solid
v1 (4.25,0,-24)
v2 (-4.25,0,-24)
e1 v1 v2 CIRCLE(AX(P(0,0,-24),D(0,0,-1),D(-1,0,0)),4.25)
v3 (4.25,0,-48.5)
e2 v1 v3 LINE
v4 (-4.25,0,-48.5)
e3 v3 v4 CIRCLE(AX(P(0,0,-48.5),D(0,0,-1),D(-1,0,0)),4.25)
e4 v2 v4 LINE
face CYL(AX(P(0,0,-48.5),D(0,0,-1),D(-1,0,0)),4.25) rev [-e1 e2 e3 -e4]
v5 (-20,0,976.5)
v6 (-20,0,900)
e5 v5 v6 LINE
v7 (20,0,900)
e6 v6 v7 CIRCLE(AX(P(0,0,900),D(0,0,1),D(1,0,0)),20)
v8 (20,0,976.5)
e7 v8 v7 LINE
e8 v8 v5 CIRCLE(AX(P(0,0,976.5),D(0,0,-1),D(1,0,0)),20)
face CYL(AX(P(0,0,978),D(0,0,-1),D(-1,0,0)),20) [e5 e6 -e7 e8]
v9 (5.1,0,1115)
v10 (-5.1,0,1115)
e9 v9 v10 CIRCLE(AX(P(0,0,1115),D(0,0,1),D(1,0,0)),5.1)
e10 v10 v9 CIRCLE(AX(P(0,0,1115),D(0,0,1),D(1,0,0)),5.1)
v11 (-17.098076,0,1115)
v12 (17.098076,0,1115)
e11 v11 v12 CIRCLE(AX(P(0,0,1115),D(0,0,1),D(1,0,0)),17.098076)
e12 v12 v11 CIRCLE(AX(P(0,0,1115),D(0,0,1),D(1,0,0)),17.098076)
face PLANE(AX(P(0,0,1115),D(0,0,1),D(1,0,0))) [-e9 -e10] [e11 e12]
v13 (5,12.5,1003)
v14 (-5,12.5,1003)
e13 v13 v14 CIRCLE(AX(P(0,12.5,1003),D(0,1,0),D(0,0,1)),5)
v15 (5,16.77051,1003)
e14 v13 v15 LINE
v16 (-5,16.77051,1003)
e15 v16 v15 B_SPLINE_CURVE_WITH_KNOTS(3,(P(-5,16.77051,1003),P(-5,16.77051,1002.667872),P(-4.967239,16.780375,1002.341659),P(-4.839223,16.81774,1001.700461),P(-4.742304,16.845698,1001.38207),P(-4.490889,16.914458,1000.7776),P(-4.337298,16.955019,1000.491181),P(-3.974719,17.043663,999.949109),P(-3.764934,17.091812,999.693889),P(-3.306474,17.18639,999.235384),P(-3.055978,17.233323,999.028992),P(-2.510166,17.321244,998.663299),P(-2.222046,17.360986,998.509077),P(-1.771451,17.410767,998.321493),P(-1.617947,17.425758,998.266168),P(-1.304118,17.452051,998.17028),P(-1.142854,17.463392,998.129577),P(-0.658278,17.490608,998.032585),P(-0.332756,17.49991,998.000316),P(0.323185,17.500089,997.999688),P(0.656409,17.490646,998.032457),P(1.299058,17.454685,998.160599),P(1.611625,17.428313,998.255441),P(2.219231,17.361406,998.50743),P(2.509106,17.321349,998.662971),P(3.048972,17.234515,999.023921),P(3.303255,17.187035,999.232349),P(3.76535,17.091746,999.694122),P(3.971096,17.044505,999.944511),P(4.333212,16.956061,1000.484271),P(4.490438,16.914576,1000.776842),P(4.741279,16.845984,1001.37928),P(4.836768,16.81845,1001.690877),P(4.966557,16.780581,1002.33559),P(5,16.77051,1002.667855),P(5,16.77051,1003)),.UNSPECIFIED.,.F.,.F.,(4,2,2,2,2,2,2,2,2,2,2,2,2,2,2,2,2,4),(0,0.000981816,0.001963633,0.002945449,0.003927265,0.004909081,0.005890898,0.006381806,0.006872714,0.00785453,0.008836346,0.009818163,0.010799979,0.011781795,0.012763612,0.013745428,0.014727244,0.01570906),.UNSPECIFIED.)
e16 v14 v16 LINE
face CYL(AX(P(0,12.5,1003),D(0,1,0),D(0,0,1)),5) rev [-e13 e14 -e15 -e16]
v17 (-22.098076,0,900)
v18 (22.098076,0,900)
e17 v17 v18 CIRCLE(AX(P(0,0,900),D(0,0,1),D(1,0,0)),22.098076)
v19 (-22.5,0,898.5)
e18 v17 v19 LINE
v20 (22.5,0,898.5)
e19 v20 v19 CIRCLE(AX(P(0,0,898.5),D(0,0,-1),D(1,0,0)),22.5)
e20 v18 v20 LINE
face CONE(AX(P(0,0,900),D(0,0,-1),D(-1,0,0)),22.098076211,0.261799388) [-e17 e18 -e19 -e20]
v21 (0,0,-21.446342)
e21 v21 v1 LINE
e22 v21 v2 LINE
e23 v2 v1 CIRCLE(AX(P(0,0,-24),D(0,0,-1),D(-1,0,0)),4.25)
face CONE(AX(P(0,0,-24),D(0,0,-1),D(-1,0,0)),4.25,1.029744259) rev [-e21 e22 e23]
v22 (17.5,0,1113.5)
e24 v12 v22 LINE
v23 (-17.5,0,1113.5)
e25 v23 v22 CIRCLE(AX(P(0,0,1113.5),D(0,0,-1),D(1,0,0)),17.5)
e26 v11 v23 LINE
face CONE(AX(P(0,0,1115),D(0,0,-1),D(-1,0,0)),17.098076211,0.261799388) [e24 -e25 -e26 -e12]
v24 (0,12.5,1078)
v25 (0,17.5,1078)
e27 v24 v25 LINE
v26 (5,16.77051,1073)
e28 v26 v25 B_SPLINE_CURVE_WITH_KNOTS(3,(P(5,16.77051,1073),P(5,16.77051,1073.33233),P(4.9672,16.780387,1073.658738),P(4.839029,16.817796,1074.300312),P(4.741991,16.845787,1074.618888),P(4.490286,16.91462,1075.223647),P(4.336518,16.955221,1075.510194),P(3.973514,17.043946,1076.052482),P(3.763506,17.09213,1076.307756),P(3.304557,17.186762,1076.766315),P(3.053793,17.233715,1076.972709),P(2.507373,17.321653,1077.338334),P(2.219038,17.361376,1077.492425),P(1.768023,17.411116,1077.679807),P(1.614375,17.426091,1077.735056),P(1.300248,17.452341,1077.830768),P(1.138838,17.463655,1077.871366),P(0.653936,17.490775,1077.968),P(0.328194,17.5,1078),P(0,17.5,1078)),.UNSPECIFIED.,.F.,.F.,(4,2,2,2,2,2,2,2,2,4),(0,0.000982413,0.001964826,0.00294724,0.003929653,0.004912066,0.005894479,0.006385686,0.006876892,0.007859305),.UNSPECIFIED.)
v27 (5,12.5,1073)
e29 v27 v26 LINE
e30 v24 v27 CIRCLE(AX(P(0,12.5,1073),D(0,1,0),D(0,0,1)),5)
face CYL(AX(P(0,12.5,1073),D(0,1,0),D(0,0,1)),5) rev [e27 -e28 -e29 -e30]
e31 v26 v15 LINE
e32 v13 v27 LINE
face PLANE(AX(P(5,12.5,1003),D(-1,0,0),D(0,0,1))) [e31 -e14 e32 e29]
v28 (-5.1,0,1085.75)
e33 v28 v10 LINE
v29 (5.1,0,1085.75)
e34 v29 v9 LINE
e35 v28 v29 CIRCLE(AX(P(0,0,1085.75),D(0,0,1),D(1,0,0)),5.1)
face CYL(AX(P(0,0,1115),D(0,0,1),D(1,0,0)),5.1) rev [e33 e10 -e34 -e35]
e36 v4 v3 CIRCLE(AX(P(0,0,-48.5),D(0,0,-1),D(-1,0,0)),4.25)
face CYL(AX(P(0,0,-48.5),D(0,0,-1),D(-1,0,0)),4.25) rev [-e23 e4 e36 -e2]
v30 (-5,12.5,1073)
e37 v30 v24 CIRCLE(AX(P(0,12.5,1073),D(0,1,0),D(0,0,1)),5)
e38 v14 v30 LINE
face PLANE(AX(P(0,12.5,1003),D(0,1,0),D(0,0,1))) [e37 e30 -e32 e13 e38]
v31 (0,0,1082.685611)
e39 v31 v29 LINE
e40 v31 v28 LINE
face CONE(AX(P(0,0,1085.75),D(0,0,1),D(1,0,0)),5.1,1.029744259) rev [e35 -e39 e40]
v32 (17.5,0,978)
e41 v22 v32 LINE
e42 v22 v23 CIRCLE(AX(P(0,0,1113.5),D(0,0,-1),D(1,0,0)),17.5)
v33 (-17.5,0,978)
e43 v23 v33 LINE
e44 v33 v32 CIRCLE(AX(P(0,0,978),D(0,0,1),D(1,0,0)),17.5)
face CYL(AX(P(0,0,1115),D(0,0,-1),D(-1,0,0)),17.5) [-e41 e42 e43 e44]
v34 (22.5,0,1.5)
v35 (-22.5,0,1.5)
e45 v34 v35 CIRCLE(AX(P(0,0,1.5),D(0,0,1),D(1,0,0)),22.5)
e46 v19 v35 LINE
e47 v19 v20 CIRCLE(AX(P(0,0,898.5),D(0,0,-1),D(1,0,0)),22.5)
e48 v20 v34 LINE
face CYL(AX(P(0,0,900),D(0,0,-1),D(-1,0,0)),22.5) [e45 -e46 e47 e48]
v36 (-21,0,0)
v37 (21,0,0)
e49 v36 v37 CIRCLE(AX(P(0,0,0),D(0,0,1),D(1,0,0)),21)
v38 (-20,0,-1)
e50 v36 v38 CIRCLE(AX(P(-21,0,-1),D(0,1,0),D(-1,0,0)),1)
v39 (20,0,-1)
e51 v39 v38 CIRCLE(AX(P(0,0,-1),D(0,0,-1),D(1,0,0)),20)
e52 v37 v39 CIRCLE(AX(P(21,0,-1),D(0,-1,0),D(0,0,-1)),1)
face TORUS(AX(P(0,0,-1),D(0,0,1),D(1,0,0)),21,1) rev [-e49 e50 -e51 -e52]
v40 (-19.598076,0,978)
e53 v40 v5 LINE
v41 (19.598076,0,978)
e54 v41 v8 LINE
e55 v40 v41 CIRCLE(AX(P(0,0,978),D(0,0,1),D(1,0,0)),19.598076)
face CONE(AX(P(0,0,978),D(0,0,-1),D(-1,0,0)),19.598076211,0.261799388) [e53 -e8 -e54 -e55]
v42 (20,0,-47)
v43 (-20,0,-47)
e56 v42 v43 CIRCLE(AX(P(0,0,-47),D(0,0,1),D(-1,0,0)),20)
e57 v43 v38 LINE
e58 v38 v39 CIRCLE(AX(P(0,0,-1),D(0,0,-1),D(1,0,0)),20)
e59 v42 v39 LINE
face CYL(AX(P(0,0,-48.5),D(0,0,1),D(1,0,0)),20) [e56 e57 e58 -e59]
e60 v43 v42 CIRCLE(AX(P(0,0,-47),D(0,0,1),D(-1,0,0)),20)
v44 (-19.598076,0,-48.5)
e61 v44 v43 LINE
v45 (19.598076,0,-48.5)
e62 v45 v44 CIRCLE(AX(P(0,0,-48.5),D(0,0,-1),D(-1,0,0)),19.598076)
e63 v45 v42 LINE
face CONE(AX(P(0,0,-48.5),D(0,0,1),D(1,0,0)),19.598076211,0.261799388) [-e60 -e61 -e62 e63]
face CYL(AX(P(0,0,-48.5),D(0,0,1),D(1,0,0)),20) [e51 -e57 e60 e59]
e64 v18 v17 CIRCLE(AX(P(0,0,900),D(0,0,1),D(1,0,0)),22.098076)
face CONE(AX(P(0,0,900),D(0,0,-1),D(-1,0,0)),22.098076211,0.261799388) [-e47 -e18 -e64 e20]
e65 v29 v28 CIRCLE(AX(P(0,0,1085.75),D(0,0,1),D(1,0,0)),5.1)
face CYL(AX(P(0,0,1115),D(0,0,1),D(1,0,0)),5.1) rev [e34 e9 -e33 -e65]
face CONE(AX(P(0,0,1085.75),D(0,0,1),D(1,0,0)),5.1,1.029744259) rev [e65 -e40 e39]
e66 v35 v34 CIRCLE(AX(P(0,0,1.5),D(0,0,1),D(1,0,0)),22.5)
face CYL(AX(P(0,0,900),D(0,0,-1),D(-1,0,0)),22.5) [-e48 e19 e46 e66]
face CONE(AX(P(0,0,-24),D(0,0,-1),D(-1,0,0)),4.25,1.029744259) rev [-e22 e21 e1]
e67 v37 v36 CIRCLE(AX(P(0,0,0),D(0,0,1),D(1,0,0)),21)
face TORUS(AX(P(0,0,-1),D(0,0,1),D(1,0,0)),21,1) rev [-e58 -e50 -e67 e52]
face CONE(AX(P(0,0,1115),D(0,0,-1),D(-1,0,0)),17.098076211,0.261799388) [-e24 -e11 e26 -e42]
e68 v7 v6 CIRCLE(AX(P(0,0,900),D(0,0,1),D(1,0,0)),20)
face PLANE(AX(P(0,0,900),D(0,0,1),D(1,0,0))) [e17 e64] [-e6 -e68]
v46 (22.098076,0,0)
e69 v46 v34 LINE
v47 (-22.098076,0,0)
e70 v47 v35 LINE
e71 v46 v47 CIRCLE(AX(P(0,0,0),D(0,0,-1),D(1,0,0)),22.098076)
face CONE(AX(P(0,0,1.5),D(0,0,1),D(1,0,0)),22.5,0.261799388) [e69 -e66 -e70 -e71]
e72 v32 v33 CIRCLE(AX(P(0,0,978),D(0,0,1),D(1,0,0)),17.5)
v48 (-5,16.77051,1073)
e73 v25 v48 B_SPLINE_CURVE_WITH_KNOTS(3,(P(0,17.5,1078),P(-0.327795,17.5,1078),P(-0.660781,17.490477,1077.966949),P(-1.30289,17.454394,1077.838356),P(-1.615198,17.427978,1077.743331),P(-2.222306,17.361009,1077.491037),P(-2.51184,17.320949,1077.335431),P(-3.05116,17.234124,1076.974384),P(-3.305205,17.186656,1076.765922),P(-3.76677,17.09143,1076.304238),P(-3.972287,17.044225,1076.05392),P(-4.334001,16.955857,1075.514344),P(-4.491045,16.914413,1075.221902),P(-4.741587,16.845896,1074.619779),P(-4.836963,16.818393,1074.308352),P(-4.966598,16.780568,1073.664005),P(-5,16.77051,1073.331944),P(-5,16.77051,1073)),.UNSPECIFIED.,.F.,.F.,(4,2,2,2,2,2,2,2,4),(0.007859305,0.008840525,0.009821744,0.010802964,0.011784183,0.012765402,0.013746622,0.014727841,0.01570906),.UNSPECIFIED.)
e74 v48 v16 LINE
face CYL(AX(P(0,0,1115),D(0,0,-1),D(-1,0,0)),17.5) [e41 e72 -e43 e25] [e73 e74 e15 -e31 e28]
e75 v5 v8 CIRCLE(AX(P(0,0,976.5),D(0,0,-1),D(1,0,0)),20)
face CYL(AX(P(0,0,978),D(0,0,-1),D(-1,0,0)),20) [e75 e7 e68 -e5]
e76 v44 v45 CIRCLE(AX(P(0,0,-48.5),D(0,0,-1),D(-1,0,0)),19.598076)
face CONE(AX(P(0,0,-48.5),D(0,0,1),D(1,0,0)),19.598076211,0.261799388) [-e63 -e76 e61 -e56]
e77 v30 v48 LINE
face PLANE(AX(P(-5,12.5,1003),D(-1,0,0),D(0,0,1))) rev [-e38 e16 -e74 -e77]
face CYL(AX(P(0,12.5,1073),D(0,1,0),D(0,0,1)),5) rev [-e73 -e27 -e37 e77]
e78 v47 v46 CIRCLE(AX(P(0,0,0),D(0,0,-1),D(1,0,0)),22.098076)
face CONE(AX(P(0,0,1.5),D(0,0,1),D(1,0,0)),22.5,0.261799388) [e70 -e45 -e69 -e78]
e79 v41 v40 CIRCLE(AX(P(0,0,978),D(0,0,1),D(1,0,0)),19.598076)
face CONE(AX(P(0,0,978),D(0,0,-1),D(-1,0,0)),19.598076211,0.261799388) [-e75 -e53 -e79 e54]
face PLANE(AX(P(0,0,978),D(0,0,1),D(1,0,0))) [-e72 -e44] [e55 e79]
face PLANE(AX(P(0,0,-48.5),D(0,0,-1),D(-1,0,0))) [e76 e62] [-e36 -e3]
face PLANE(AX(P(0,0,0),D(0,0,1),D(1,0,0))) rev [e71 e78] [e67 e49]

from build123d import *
from OCP.BRepFilletAPI import BRepFilletAPI_MakeChamfer

# Parameters (mm, degrees)
SKETCH_1_R              = 22.5
EXTRUDE_1_DEPTH         = 900
SKETCH_2_R              = 20
EXTRUDE_2_DEPTH         = 78
SKETCH_3_R              = 17.5
EXTRUDE_3_DEPTH         = 137
EXTRUDE_START           = 48.5
SKETCH_4_R              = 20
EXTRUDE_4_DEPTH         = 48.5
CHAMFER_1_SIZE          = 1.5
CHAMFER_1_SIZE2         = 0.401923789
CUT_EXTRUDE_1_DEPTH     = 5
HOLE_WIZARD_M12_1_D     = 10.2
HOLE_WIZARD_M12_1_DEPTH = 29.25
HOLE_WIZARD_M12_1_TIP   = 3.064389157
HOLE_WIZARD_M10_1_D     = 8.5
HOLE_WIZARD_M10_1_DEPTH = 24.5
HOLE_WIZARD_M10_1_TIP   = 2.553657631
CHAMFER_2_SIZE          = 1.5
CHAMFER_2_SIZE2         = 0.401923789
FILLET_1_R              = 1


with BuildPart() as part:
    # 草图1 → 凸台-拉伸1 (new body)
    with BuildSketch(Plane.XY):
        Circle(SKETCH_1_R)
    extrude(amount=EXTRUDE_1_DEPTH)

    # 草图2 → 凸台-拉伸2 (add)
    with BuildSketch(Plane.XY.offset(900)):
        Circle(SKETCH_2_R)
    extrude(amount=EXTRUDE_2_DEPTH)

    # 草图3 → 凸台-拉伸3 (add)
    with BuildSketch(Plane.XY.offset(978)):
        Circle(SKETCH_3_R)
    extrude(amount=EXTRUDE_3_DEPTH)

    # 草图4 → 凸台-拉伸4 (add)
    with BuildSketch(Plane(origin=(0, 0, 0), x_dir=(-1, 0, 0), z_dir=(0, 0, -1)).offset(EXTRUDE_START)):
        with Locations(Location((0, 0, 0), (0, 0, 180))):
            Circle(SKETCH_4_R)
    extrude(amount=-EXTRUDE_4_DEPTH)

    # 倒角1: one chamfer whose edges measure the first distance from different faces: ONE call of the kernel's chamfer builder (chamfer() names one face for all edges)
    chamfer_1_edges_1 = [part.edges().sort_by_distance(p)[0] for p in [
        (-17.5, 0, 1115),
    ]]
    chamfer_1_side_1 = [part.faces().sort_by_distance(p)[0] for p in [
        (-17.5, 0, 1046.5),
    ]]
    chamfer_1_edges_2 = [part.edges().sort_by_distance(p)[0] for p in [
        (-20, 0, -48.5),
    ]]
    chamfer_1_side_2 = [part.faces().sort_by_distance(p)[0] for p in [
        (-20, 0, -24.25),
    ]]
    chamfer_1_edges_3 = [part.edges().sort_by_distance(p)[0] for p in [
        (-22.5, 0, 900),
    ]]
    chamfer_1_side_3 = [part.faces().sort_by_distance(p)[0] for p in [
        (-22.5, 0, 450),
    ]]
    chamfer_1_edges_4 = [part.edges().sort_by_distance(p)[0] for p in [
        (-20, 0, 978),
    ]]
    chamfer_1_side_4 = [part.faces().sort_by_distance(p)[0] for p in [
        (-20, 0, 939),
    ]]
    chamfer_1 = BRepFilletAPI_MakeChamfer(part.part.solid().wrapped)
    for e in chamfer_1_edges_1:
        chamfer_1.Add(CHAMFER_1_SIZE, CHAMFER_1_SIZE2, e.wrapped, chamfer_1_side_1[0].wrapped)  # the first distance lies on this face
    for e in chamfer_1_edges_2:
        chamfer_1.Add(CHAMFER_1_SIZE, CHAMFER_1_SIZE2, e.wrapped, chamfer_1_side_2[0].wrapped)  # the first distance lies on this face
    for e in chamfer_1_edges_3:
        chamfer_1.Add(CHAMFER_1_SIZE, CHAMFER_1_SIZE2, e.wrapped, chamfer_1_side_3[0].wrapped)  # the first distance lies on this face
    for e in chamfer_1_edges_4:
        chamfer_1.Add(CHAMFER_1_SIZE, CHAMFER_1_SIZE2, e.wrapped, chamfer_1_side_4[0].wrapped)  # the first distance lies on this face
    add(Compound.cast(chamfer_1.Shape()), mode=Mode.REPLACE)

    # 草图5 → 切除-拉伸1 (cut)
    with BuildSketch(Plane(origin=(0, 17.5, 0), x_dir=(1, 0, 0), z_dir=(0, 1, 0))):
        with BuildLine():
            Line((5, -1003), (5, -1073))
            ThreePointArc((5, -1073), (0, -1078), (-5, -1073))
            Line((-5, -1073), (-5, -1003))
            ThreePointArc((-5, -1003), (0, -998), (5, -1003))
        make_face()
    extrude(amount=-CUT_EXTRUDE_1_DEPTH, mode=Mode.SUBTRACT)

    # M12 螺纹孔1
    with Locations(Plane.XY.offset(1115)):
        with Locations((0, 0)):
            Hole(HOLE_WIZARD_M12_1_D / 2, depth=HOLE_WIZARD_M12_1_DEPTH)
            with Locations((0, 0, -(HOLE_WIZARD_M12_1_DEPTH + HOLE_WIZARD_M12_1_TIP / 2))):  # 118° drill point
                Cone(0, HOLE_WIZARD_M12_1_D / 2, HOLE_WIZARD_M12_1_TIP, mode=Mode.SUBTRACT)

    # M10 螺纹孔1
    with Locations(Plane(origin=(0, 0, -48.5), x_dir=(-1, 0, 0), z_dir=(0, 0, -1))):
        with Locations((0, 0)):
            Hole(HOLE_WIZARD_M10_1_D / 2, depth=HOLE_WIZARD_M10_1_DEPTH)
            with Locations((0, 0, -(HOLE_WIZARD_M10_1_DEPTH + HOLE_WIZARD_M10_1_TIP / 2))):  # 118° drill point
                Cone(0, HOLE_WIZARD_M10_1_D / 2, HOLE_WIZARD_M10_1_TIP, mode=Mode.SUBTRACT)

    # 倒角2
    chamfer_2_edges = [part.edges().sort_by_distance(p)[0] for p in [
        (-22.5, 0, 0),
    ]]
    chamfer_2_side = [part.faces().sort_by_distance(p)[0] for p in [
        (-22.5, 0, 449.25),
    ]]
    chamfer(chamfer_2_edges, length=CHAMFER_2_SIZE, length2=CHAMFER_2_SIZE2, reference=chamfer_2_side[0])

    # 圆角1
    fillet_1_edges = [part.edges().sort_by_distance(p)[0] for p in [
        (-20, 0, 0),
    ]]
    fillet(fillet_1_edges, radius=FILLET_1_R)


solid = part.part
